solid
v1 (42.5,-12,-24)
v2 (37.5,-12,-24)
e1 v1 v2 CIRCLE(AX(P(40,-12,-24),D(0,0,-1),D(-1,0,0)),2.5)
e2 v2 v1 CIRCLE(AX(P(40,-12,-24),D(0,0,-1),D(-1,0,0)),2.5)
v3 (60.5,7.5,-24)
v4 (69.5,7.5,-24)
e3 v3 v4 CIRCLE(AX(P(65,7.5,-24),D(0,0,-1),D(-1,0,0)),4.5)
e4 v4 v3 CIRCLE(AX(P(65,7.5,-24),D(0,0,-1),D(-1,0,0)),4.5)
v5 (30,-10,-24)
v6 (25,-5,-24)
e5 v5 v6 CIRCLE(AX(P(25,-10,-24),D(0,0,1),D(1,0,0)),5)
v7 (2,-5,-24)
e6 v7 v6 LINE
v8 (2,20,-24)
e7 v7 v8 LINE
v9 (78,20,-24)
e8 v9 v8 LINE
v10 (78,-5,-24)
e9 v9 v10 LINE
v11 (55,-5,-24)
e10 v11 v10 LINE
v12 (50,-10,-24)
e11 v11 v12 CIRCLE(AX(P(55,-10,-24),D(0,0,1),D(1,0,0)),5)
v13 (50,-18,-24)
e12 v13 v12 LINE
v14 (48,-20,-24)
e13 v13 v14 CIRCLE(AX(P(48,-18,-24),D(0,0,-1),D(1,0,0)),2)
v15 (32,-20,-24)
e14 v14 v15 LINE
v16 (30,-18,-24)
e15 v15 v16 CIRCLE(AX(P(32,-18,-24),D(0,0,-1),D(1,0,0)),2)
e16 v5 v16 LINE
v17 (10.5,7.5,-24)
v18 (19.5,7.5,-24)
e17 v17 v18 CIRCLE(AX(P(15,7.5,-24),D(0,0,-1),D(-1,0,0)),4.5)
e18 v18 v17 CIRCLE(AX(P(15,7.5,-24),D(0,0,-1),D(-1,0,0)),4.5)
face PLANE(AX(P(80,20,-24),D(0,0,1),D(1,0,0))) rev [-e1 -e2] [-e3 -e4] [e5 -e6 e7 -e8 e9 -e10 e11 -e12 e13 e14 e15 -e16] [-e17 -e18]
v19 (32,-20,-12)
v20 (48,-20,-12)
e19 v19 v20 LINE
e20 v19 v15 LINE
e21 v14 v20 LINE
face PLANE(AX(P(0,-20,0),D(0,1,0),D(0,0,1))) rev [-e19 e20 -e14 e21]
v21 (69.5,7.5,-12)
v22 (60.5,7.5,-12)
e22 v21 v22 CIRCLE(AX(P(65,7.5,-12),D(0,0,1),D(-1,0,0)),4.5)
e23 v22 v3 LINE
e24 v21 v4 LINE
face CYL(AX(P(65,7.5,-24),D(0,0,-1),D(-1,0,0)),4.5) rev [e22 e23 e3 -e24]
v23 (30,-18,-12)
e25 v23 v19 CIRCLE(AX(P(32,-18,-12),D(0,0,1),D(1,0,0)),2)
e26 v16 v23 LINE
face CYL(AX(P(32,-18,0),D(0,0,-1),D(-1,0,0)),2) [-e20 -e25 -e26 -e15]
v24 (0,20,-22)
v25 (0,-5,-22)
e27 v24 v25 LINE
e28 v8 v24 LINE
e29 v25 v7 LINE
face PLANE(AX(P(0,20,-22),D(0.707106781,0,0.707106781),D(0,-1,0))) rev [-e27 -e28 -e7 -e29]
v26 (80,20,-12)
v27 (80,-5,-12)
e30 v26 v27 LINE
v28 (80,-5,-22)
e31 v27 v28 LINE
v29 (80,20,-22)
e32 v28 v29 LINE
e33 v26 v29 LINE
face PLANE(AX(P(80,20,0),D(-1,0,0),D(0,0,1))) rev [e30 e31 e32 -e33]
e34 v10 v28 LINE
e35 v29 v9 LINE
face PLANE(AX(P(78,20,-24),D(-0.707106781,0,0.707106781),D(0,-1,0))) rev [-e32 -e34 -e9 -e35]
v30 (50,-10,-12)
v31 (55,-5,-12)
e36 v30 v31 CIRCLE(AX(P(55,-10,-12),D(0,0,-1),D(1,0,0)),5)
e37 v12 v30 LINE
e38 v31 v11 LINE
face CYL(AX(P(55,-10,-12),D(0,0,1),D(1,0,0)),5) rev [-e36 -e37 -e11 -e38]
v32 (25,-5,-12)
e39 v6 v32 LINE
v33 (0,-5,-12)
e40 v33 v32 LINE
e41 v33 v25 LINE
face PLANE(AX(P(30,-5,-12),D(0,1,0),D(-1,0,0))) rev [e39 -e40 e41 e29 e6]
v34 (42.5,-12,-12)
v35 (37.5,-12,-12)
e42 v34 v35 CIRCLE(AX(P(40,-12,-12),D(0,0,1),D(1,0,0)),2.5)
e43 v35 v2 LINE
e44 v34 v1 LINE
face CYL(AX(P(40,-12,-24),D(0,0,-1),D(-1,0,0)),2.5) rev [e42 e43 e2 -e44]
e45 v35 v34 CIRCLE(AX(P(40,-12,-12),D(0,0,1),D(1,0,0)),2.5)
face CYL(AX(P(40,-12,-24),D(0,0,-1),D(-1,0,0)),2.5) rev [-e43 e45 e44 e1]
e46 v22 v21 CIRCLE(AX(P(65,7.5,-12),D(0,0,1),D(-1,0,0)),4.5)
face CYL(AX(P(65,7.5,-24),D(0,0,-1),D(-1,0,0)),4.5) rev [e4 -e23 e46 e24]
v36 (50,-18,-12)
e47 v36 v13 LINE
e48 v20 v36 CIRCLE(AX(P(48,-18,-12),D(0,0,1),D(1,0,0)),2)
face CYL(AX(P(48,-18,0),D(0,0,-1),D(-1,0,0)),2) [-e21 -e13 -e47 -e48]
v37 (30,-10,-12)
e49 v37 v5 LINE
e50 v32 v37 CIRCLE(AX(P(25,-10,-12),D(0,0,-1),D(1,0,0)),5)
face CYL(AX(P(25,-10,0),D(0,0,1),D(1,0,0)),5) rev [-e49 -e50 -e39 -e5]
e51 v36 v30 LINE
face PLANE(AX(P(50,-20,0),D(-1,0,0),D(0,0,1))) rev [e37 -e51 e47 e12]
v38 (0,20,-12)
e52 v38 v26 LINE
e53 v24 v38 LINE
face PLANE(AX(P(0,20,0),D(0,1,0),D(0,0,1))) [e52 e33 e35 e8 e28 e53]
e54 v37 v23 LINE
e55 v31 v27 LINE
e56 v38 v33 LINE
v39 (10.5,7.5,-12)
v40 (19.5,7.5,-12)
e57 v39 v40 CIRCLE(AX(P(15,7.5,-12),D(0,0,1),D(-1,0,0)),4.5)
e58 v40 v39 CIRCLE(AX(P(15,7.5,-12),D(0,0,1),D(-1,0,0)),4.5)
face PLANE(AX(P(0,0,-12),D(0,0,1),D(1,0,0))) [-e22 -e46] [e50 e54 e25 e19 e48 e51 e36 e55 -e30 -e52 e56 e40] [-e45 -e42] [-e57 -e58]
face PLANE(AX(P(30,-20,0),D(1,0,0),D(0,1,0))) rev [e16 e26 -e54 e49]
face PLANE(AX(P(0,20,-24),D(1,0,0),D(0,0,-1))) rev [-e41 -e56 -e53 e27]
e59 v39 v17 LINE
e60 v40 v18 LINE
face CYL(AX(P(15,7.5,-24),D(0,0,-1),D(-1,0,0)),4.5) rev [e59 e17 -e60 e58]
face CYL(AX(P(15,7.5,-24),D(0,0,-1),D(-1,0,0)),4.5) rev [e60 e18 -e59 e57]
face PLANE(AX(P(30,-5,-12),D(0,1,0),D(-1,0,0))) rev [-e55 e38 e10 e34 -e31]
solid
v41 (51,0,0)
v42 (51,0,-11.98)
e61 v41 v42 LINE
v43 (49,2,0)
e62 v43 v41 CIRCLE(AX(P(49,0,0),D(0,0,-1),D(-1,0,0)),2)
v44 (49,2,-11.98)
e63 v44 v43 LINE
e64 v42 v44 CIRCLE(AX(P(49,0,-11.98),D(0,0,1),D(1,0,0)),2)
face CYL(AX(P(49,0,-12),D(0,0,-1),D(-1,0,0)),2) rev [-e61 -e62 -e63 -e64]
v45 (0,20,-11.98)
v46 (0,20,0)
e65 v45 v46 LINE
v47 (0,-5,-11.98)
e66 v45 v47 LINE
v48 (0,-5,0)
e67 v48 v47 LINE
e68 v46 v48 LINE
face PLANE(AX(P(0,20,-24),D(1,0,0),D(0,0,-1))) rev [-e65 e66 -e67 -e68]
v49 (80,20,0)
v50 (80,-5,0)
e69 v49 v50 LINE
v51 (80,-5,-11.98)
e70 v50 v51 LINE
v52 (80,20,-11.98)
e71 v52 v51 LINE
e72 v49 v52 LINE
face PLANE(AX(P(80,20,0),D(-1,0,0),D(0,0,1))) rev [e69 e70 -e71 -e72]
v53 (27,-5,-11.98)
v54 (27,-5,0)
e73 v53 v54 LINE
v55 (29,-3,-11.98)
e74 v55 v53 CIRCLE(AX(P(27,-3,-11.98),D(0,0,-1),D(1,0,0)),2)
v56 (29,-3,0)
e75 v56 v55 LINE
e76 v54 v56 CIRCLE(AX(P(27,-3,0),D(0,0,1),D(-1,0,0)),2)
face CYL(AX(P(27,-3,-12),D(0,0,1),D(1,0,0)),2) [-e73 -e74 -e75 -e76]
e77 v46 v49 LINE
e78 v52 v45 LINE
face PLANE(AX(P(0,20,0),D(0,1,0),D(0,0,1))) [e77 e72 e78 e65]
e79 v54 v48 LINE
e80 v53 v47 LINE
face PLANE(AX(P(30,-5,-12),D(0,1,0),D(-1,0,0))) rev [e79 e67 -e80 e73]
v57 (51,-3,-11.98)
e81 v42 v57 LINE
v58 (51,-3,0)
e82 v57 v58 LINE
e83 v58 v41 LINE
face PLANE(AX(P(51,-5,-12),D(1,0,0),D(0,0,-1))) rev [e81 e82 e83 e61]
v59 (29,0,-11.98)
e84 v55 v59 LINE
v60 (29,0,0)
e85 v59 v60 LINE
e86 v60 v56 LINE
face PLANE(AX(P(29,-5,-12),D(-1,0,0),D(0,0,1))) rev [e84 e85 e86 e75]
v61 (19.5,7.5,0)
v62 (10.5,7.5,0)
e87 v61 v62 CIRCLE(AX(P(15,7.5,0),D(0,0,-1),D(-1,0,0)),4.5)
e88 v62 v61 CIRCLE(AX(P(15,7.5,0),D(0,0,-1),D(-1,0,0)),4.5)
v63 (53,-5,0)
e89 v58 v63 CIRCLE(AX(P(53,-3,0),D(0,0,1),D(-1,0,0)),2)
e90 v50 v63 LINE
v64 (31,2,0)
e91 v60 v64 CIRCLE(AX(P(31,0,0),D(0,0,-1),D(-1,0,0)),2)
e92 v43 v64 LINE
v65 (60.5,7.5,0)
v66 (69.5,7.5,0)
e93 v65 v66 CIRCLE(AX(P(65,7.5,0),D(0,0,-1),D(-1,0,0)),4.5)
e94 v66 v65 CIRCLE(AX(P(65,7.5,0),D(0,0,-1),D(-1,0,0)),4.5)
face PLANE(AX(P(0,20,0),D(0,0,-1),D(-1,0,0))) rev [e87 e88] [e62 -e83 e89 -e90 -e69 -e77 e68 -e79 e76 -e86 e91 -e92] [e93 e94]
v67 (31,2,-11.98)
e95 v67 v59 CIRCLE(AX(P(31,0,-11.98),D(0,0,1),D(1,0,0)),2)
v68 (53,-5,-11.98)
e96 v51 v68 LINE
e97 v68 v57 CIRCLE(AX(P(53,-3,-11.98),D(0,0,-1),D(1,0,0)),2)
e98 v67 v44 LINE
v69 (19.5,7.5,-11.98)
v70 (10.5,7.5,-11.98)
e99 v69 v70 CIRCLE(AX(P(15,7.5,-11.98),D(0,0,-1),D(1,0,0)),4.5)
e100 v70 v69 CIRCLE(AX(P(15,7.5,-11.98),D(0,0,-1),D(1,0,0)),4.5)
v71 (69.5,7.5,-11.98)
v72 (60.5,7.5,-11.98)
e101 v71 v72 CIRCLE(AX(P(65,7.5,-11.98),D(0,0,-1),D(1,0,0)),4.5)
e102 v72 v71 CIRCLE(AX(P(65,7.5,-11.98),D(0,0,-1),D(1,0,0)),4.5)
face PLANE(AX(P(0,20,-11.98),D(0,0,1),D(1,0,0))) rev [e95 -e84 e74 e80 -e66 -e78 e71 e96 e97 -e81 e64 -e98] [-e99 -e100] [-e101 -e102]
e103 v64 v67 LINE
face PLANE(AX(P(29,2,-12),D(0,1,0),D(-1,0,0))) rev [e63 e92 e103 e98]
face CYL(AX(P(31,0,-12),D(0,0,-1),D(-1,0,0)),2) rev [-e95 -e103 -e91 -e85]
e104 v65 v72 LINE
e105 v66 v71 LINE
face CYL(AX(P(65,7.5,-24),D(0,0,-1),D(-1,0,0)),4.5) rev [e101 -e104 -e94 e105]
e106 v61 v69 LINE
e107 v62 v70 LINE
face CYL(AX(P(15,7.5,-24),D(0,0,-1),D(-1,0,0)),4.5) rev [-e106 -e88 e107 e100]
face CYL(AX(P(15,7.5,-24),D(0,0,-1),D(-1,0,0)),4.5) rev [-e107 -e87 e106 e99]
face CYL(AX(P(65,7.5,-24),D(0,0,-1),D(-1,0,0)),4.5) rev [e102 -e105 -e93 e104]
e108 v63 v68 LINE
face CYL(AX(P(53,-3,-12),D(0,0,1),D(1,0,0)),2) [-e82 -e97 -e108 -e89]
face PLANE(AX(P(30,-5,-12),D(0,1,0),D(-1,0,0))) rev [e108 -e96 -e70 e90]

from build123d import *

# Parameters (mm, degrees)
SKETCH1_W                = 80
SKETCH1_H                = 24
BOSS_EXTRUDE1_DEPTH      = 20
CHAMFER1_SIZE            = 2
SKETCH9_W                = 20
SKETCH9_H                = 15
CUT_EXTRUDE1_DEPTH       = 12
M6_TAPPED_HOLE1_D        = 5
M6_TAPPED_HOLE1_DEPTH    = 15
M6_TAPPED_HOLE1_TIP      = 1.502151548
M8_CLEARANCE_HOLE1_D     = 9
M8_CLEARANCE_HOLE1_DEPTH = 30
M8_CLEARANCE_HOLE1_TIP   = 2.703872786
SKETCH16_W               = 30
SKETCH16_H               = 15
CUT_EXTRUDE2_DEPTH       = 86.883642214
FILLET1_R                = 5
FILLET2_R                = 2
SKETCH17_W               = 22
SKETCH17_H               = 7
CUT_EXTRUDE3_DEPTH       = 12
SKETCH18_W               = 80
SKETCH18_H               = 0.02
CUT_EXTRUDE4_DEPTH       = 88.183714076
FILLET3_R                = 2


with BuildPart() as part:
    # Sketch1 → Boss-Extrude1 (new, symmetric)
    with BuildSketch(Plane(origin=(0, 0, 0), x_dir=(1, 0, 0), z_dir=(0, 1, 0))):
        with Locations((40, 12)):
            Rectangle(SKETCH1_W, SKETCH1_H)
    extrude(amount=BOSS_EXTRUDE1_DEPTH, both=True)

    # Chamfer1
    chamfer1_edges = [part.edges().sort_by_distance(p)[0] for p in [
        (0, 0, -24),
        (80, 0, -24),
    ]]
    chamfer(chamfer1_edges, length=CHAMFER1_SIZE)

    # Sketch9 → Cut-Extrude1 (cut)
    with BuildSketch(Plane.XY):
        with Locations((40, -12.5)):
            Rectangle(SKETCH9_W, SKETCH9_H)
    extrude(amount=-CUT_EXTRUDE1_DEPTH, mode=Mode.SUBTRACT)

    # M6 Tapped Hole1
    with Locations(Plane(origin=(0, 0, -24), x_dir=(-1, 0, 0), z_dir=(0, 0, -1))):
        with Locations((-40, -12)):
            Hole(M6_TAPPED_HOLE1_D / 2, depth=M6_TAPPED_HOLE1_DEPTH)
            with Locations((0, 0, -(M6_TAPPED_HOLE1_DEPTH + M6_TAPPED_HOLE1_TIP / 2))):  # 118° drill point
                Cone(0, M6_TAPPED_HOLE1_D / 2, M6_TAPPED_HOLE1_TIP, mode=Mode.SUBTRACT)

    # M8 Clearance Hole1
    with Locations(Plane(origin=(0, 0, -24), x_dir=(-1, 0, 0), z_dir=(0, 0, -1))):
        with Locations((-65, 7.5), (-15, 7.5)):
            Hole(M8_CLEARANCE_HOLE1_D / 2, depth=M8_CLEARANCE_HOLE1_DEPTH)
            with Locations((0, 0, -(M8_CLEARANCE_HOLE1_DEPTH + M8_CLEARANCE_HOLE1_TIP / 2))):  # 118° drill point
                Cone(0, M8_CLEARANCE_HOLE1_D / 2, M8_CLEARANCE_HOLE1_TIP, mode=Mode.SUBTRACT)

    # Sketch16 → Cut-Extrude2 (cut, through all)
    with BuildSketch(Plane(origin=(0, 0, -24), x_dir=(-1, 0, 0), z_dir=(0, 0, -1))):
        with Locations((-65, -12.5)):
            Rectangle(SKETCH16_W, SKETCH16_H)
        with Locations((-15, -12.5)):
            Rectangle(SKETCH16_W, SKETCH16_H)
    extrude(amount=-CUT_EXTRUDE2_DEPTH, mode=Mode.SUBTRACT)

    # Fillet1
    fillet1_edges = [part.edges().sort_by_distance(p)[0] for p in [
        (50, -5, -18),
        (30, -5, -18),
    ]]
    fillet(fillet1_edges, radius=FILLET1_R)

    # Fillet2
    fillet2_edges = [part.edges().sort_by_distance(p)[0] for p in [
        (50, -20, -18),
        (30, -20, -18),
    ]]
    fillet(fillet2_edges, radius=FILLET2_R)

    # Sketch17 → Cut-Extrude3 (cut)
    with BuildSketch(Plane.XY):
        with Locations((40, -1.5)):
            Rectangle(SKETCH17_W, SKETCH17_H)
    extrude(amount=-CUT_EXTRUDE3_DEPTH, mode=Mode.SUBTRACT)

    # Sketch18 → Cut-Extrude4 (cut, through all)
    with BuildSketch(Plane.XZ.offset(5)):
        with Locations((40, -11.99)):
            Rectangle(SKETCH18_W, SKETCH18_H)
    extrude(amount=-CUT_EXTRUDE4_DEPTH, mode=Mode.SUBTRACT)


with BuildPart() as cut_extrude4_piece_1:
    # of the separate pieces the step leaves, piece 1, a body of its own (cut_extrude4_pieces)
    add(part.part.solids().sort_by_distance((50, -18, -24))[0])


with BuildPart() as cut_extrude4_piece_2:
    # of the separate pieces the step leaves, piece 2, a body of its own (cut_extrude4_pieces)
    add(part.part.solids().sort_by_distance((51, -5, -11.98))[0])

    # Fillet3
    fillet3_edges = [cut_extrude4_piece_2.edges().sort_by_distance(p)[0] for p in [
        (51, 2, -5.99),
        (51, -5, -5.99),
        (29, 2, -5.99),
        (29, -5, -5.99),
    ]]
    fillet(fillet3_edges, radius=FILLET3_R)


solid = Compound([cut_extrude4_piece_1.part, cut_extrude4_piece_2.part])
